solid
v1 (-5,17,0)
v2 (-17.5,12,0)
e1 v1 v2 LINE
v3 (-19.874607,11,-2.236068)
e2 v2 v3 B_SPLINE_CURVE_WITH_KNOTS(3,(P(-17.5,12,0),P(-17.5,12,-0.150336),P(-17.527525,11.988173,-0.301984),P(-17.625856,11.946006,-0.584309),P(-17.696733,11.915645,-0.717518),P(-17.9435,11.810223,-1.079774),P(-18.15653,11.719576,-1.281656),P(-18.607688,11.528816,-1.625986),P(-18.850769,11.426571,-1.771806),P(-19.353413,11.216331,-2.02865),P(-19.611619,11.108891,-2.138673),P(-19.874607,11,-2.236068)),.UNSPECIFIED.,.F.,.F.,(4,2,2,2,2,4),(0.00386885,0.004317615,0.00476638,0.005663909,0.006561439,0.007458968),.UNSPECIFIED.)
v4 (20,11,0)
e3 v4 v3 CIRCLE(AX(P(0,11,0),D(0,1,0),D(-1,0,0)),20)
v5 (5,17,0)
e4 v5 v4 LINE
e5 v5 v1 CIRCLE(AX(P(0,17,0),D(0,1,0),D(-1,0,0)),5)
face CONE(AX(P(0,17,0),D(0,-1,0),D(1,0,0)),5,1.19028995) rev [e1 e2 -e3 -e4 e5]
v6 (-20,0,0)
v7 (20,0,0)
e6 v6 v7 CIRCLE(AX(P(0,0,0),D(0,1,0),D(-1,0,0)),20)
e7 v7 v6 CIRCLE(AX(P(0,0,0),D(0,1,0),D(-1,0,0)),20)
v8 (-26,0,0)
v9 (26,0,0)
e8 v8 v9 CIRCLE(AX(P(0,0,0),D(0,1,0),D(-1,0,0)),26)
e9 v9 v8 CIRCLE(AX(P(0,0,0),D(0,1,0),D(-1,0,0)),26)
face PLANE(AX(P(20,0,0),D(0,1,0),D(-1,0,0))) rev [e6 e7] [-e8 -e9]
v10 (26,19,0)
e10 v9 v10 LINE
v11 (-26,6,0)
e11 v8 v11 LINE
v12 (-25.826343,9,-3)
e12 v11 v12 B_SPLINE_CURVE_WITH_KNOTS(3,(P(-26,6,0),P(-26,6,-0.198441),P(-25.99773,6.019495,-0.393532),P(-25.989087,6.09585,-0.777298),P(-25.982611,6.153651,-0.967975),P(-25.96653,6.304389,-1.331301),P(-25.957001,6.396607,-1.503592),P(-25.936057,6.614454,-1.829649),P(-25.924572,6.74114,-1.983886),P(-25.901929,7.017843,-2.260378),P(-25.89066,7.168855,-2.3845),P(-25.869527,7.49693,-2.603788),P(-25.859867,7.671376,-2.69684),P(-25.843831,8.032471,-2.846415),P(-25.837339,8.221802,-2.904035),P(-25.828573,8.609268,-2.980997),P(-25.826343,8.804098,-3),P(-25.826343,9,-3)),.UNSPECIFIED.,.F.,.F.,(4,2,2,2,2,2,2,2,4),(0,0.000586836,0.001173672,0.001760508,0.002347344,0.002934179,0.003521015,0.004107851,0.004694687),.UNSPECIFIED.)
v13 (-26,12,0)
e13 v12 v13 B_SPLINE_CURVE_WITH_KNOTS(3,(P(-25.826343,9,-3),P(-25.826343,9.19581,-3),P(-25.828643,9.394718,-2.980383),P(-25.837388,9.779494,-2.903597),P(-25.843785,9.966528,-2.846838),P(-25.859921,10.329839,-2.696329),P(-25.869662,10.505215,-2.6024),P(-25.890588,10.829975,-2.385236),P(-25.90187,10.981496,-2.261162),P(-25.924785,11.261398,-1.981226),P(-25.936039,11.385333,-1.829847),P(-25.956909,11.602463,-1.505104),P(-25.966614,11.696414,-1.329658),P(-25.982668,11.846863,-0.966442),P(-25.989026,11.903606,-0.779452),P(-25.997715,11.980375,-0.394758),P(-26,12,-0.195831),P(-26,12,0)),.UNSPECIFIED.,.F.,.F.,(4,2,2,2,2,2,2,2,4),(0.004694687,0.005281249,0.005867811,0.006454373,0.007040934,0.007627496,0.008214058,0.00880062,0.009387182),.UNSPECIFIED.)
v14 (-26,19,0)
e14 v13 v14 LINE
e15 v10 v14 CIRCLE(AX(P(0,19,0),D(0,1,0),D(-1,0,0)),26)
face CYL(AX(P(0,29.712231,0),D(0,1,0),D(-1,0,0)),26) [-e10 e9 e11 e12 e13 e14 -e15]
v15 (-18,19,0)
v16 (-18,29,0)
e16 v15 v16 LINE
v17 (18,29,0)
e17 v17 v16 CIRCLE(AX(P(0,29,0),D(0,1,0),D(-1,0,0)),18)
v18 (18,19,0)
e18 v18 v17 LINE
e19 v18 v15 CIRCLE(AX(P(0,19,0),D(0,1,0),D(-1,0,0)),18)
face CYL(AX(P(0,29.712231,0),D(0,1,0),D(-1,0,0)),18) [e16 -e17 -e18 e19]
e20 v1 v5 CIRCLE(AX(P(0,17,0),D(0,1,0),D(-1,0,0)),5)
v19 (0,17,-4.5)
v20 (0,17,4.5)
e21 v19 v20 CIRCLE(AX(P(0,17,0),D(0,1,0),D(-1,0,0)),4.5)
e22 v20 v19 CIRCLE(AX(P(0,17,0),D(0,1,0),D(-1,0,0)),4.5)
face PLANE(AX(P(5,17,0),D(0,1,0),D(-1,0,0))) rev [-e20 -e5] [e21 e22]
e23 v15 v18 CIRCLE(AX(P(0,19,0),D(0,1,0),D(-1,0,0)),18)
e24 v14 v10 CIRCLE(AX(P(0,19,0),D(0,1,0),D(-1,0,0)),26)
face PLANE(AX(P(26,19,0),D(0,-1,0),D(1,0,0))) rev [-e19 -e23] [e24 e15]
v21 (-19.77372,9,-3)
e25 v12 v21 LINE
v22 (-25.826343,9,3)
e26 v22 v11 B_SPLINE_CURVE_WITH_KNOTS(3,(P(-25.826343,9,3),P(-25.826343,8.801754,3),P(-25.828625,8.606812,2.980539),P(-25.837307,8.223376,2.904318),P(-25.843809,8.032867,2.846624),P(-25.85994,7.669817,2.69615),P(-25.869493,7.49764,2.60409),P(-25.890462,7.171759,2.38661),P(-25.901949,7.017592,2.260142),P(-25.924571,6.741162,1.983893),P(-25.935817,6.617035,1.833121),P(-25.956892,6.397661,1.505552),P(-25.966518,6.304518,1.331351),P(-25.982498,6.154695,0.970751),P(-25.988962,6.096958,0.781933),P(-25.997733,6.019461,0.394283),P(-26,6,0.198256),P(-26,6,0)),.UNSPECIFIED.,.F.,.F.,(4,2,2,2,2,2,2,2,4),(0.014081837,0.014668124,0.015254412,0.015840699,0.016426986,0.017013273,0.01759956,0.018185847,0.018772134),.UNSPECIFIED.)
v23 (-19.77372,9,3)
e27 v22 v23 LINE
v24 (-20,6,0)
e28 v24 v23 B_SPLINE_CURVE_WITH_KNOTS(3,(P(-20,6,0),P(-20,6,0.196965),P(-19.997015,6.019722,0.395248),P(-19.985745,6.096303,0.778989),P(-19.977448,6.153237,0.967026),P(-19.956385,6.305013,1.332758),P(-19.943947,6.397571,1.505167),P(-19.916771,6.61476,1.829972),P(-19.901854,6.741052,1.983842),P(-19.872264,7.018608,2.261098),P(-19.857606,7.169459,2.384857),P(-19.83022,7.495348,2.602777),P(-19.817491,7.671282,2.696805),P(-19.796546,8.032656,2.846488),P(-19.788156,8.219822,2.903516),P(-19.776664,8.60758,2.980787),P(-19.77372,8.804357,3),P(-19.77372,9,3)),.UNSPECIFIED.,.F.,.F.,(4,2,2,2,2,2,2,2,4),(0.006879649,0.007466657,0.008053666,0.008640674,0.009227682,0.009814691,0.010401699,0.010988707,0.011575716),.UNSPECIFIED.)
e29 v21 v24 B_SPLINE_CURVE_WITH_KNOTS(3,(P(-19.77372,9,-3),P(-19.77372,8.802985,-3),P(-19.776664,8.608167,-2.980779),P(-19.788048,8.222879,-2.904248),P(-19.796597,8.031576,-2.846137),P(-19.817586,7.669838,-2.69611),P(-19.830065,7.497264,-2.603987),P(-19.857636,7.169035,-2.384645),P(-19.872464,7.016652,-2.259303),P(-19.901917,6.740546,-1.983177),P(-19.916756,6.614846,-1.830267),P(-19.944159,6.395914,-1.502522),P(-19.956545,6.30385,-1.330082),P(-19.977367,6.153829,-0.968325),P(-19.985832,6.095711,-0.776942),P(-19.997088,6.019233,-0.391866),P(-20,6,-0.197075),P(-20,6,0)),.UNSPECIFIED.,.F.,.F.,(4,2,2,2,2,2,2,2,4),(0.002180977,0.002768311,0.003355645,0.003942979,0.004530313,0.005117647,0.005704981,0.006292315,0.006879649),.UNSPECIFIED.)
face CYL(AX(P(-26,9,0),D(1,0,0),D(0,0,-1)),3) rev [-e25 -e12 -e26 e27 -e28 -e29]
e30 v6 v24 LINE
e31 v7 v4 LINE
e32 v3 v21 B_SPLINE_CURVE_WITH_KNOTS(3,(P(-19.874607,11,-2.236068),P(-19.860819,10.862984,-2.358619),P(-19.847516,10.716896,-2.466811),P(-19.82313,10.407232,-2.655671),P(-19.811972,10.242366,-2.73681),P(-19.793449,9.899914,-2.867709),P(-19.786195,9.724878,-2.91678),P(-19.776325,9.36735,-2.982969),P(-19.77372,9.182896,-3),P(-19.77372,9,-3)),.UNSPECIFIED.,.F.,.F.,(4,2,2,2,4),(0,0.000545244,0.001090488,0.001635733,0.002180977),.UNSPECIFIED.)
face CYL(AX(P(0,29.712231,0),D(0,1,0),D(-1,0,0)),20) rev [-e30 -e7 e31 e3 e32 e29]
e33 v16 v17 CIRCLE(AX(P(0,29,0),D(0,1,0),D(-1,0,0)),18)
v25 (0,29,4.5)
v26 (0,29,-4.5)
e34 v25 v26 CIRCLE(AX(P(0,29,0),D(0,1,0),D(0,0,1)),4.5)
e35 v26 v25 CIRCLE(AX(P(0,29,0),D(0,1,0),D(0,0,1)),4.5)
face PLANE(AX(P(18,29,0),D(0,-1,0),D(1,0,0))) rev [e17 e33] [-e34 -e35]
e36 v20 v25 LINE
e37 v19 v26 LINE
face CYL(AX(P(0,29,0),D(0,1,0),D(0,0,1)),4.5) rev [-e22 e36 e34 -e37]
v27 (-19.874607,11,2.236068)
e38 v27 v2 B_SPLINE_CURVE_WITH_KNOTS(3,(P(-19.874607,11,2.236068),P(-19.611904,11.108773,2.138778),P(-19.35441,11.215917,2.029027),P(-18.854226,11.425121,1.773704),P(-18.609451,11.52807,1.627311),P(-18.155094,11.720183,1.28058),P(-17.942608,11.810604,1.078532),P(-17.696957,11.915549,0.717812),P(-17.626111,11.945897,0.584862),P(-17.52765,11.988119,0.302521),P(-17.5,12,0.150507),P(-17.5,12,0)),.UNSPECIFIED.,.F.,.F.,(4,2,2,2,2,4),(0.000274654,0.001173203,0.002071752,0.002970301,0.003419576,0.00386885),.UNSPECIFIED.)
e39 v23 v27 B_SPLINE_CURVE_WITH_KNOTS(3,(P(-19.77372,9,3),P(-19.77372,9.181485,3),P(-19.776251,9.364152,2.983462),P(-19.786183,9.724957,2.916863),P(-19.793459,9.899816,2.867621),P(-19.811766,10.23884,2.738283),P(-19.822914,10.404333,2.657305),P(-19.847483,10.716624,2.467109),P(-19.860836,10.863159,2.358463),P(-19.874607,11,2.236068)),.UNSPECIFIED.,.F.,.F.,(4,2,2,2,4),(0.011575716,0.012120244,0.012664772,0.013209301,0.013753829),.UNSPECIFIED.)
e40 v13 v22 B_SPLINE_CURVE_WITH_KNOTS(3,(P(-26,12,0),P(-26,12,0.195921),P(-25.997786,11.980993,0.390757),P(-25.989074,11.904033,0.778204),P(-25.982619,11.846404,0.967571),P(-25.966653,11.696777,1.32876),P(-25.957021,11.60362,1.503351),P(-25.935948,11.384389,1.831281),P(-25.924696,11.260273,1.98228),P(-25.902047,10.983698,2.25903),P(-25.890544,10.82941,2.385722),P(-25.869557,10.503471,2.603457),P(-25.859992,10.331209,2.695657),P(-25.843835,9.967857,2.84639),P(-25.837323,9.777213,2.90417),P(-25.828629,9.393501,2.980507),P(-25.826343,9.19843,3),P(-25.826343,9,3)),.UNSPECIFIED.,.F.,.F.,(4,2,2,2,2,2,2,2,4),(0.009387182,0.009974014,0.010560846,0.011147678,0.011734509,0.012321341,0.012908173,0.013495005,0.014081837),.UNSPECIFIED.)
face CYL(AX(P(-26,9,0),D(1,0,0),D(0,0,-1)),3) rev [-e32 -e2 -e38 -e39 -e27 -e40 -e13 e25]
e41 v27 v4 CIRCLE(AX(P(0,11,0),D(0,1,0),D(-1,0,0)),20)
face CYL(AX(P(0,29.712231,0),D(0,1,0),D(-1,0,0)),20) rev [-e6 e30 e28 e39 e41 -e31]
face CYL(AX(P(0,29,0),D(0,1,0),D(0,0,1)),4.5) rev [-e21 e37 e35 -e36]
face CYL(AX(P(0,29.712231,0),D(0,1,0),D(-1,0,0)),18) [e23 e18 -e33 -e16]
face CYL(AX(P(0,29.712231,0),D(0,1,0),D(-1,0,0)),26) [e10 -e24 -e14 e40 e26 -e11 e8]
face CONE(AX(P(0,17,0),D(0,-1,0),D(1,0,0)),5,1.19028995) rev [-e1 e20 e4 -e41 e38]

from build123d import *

# Parameters (mm, degrees)
M10X1_0_1_D         = 9
SKETCH_4_R          = 3
CUT_EXTRUDE_1_DEPTH = 47.829477896


with BuildPart() as part:
    # 草图1 → 旋转1 (revolve)
    with BuildSketch(Plane.XY, mode=Mode.PRIVATE) as revolve_1_sk:
        Polygon((20, 0), (26, 0), (26, 19), (18, 19), (18, 29), (0, 29), (0, 17), (5, 17), (20, 11), align=None)
    revolve(revolve_1_sk.sketch.rotate(Axis((0, 29.712230849, 0), (0, -1, 0)), 180), axis=Axis((0, 29.712230849, 0), (0, -1, 0)))

    # M10x1.0 螺纹孔1 (through all)
    with Locations(Plane(origin=(0, 29, 0), x_dir=(1, 0, 0), z_dir=(0, 1, 0))):
        with Locations((0, 0)):
            Hole(M10X1_0_1_D / 2)

    # 草图4 → 切除-拉伸1 (cut, through all)
    with BuildSketch(Plane(origin=(0, 0, 0), x_dir=(0, 0, -1), z_dir=(1, 0, 0))):
        with Locations(Location((0, 9, 0), (0, 0, 270.000000001))):
            Circle(SKETCH_4_R)
    extrude(amount=-CUT_EXTRUDE_1_DEPTH, mode=Mode.SUBTRACT)


solid = part.part
